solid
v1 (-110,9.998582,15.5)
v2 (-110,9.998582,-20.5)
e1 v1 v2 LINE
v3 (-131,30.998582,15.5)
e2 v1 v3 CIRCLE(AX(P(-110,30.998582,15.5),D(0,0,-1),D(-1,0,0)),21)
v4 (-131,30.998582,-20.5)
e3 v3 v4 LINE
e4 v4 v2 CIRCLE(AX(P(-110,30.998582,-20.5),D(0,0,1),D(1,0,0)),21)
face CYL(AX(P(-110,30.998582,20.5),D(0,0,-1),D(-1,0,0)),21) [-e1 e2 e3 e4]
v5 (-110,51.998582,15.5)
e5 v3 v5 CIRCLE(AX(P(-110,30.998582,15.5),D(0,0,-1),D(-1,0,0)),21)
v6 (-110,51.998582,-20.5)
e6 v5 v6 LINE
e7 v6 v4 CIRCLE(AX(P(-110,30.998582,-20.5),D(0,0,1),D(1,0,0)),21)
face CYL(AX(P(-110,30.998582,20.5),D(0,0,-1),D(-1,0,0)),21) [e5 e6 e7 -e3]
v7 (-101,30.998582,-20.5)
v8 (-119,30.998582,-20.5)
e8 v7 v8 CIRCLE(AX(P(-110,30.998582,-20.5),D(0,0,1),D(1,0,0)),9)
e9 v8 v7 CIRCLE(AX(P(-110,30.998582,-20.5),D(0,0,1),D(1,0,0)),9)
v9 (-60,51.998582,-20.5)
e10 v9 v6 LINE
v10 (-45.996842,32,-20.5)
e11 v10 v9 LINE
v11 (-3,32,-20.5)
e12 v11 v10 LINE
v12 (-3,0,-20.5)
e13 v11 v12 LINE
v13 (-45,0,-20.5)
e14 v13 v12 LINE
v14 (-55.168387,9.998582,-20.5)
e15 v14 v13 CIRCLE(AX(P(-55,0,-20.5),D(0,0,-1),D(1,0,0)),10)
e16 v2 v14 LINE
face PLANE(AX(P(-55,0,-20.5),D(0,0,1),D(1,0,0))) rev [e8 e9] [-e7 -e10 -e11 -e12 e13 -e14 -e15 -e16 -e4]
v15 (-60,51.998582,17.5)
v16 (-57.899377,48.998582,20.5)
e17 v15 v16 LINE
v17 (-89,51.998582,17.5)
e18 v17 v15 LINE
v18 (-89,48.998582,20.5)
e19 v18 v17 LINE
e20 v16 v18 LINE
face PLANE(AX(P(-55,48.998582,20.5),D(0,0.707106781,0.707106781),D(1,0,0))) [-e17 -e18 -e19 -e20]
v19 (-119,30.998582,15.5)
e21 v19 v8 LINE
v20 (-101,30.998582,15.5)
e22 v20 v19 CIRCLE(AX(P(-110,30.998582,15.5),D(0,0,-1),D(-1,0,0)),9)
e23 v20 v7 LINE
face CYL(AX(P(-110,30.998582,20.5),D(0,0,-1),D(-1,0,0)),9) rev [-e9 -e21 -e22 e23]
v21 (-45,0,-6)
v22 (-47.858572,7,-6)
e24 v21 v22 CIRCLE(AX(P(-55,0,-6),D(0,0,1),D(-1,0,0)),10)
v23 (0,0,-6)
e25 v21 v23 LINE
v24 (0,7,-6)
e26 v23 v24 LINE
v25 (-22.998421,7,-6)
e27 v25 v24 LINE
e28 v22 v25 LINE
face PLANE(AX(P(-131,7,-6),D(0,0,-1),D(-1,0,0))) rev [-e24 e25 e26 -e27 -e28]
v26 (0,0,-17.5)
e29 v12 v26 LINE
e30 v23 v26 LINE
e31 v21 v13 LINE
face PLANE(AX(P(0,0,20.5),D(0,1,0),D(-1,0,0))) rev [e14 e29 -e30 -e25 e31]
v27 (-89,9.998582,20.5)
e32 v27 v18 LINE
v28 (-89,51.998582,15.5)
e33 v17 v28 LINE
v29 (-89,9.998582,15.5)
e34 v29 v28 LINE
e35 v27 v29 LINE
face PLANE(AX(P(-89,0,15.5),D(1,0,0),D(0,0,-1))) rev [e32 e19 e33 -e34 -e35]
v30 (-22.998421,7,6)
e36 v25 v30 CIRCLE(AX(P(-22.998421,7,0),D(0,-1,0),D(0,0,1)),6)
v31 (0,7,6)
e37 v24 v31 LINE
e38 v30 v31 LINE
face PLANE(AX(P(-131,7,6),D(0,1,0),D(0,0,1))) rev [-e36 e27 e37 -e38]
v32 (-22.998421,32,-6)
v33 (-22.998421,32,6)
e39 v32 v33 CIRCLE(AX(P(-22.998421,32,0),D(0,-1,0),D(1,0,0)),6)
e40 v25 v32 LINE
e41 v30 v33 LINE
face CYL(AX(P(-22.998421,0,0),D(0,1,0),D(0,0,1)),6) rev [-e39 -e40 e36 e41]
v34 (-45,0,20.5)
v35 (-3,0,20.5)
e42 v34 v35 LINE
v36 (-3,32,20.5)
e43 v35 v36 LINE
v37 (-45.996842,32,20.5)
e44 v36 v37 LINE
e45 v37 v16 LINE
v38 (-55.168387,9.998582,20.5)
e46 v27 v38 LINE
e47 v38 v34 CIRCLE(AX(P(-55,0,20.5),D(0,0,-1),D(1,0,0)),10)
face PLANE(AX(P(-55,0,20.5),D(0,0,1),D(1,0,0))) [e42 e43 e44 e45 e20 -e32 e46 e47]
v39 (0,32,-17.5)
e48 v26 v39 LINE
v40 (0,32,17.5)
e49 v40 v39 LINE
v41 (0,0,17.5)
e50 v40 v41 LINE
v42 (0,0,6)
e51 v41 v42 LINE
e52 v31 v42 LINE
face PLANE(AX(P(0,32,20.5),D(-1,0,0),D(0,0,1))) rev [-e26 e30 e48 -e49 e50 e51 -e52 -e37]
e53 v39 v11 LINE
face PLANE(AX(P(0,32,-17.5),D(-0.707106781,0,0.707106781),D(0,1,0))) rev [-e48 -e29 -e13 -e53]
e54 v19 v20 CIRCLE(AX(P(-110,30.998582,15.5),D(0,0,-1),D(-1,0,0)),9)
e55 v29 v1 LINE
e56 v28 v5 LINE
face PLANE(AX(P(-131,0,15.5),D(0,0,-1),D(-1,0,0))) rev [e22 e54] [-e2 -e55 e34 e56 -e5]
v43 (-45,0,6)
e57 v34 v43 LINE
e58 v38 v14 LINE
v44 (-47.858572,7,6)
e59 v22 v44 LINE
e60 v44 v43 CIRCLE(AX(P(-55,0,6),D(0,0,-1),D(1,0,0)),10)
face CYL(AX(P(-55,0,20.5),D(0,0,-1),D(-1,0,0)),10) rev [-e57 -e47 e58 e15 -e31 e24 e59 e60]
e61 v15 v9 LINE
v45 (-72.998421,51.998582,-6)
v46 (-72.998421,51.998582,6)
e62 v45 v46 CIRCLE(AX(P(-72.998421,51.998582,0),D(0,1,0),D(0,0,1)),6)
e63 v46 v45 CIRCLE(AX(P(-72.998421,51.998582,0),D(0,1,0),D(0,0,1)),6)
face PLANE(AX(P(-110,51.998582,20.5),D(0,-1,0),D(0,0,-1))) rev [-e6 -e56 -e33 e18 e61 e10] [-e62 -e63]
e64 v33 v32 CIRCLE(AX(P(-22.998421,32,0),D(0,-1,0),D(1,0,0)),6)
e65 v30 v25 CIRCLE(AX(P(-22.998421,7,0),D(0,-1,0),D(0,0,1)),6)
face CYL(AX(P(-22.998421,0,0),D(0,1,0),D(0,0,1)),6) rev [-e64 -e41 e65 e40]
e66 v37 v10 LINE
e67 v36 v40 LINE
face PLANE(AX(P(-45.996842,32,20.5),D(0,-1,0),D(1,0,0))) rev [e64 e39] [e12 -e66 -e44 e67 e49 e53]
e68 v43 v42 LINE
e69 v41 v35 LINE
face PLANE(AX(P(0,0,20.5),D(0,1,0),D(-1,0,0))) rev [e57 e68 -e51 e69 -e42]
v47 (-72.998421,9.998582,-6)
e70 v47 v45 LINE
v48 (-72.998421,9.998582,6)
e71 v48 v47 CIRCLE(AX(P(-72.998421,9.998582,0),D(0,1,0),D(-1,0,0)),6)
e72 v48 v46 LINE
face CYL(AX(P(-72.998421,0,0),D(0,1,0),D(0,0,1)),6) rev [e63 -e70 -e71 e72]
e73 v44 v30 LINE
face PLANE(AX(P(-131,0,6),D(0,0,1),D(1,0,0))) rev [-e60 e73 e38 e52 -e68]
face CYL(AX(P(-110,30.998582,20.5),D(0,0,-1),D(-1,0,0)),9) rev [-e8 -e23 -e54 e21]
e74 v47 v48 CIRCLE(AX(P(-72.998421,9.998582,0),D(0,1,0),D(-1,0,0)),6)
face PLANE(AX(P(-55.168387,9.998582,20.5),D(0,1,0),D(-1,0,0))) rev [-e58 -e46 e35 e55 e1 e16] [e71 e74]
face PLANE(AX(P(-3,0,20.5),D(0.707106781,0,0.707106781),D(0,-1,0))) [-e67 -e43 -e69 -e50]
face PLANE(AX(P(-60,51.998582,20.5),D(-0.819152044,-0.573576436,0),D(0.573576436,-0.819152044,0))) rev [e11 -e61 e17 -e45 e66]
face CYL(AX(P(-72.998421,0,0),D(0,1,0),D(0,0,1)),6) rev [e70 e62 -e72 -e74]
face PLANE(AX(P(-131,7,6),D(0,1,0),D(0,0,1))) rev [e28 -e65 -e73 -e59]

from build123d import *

# Parameters (mm, degrees)
BRACKET_SIDE_PROFILE_SKETCH_R = 9
BRACKET_BODY_41MM_DEPTH       = 20.5
TOP_FACE_CUTS_SKETCH_R        = 6
TOP_FACE_CUTS_SKETCH_W        = 42
TOP_FACE_CUTS_SKETCH_H        = 5
TOP_FACE_CUTS_DEPTH           = 143.425779095
END_SLOT_SKETCH_W             = 12
END_SLOT_SKETCH_H             = 7
END_SLOT_12MM_DEPTH           = 143.425779095
EDGE_CHAMFER_3MM_SIZE         = 3


with BuildPart() as part:
    # Bracket Side Profile Sketch → Bracket Body 41mm (new, symmetric)
    with BuildSketch(Plane.XY):
        with BuildLine():
            Line((0, 0), (-45, 0))
            ThreePointArc((-45, 0), (-47.988718556, 7.130352903), (-55.168386504, 9.998582199))
            Line((-55.168386504, 9.998582199), (-86.000956968, 9.998582199))
            Line((-86.000956968, 9.998582199), (-110, 9.998582199))
            ThreePointArc((-110, 9.998582199), (-131, 30.998582199), (-110, 51.998582199))
            Line((-110, 51.998582199), (-85.996841991, 51.998582199))
            Line((-85.996841991, 51.998582199), (-60, 51.998582199))
            Line((-60, 51.998582199), (-45.996841991, 32))
            Line((-45.996841991, 32), (0, 32))
            Line((0, 32), (0, 0))
        make_face()
        with Locations((-110, 30.998582199)):
            Circle(BRACKET_SIDE_PROFILE_SKETCH_R, mode=Mode.SUBTRACT)
    extrude(amount=BRACKET_BODY_41MM_DEPTH, both=True)

    # Top Face Cuts Sketch → Top Face Cuts (cut, through all)
    with BuildSketch(Plane(origin=(0, 51.998582199, 0), x_dir=(1, 0, 0), z_dir=(0, 1, 0))):
        with Locations(Location((-72.998420995, 0, 0), (0, 0, 270))):
            Circle(TOP_FACE_CUTS_SKETCH_R)
        with Locations(Location((-22.998420995, 0, 0), (0, 0, 270))):
            Circle(TOP_FACE_CUTS_SKETCH_R)
        with Locations((-110, -18)):
            Rectangle(TOP_FACE_CUTS_SKETCH_W, TOP_FACE_CUTS_SKETCH_H)
    extrude(amount=-TOP_FACE_CUTS_DEPTH, mode=Mode.SUBTRACT)

    # End Slot Sketch → End Slot 12mm (cut, through all)
    with BuildSketch(Plane(origin=(0, 0, 0), x_dir=(0, 0, -1), z_dir=(1, 0, 0))):
        with Locations((0, 3.5)):
            Rectangle(END_SLOT_SKETCH_W, END_SLOT_SKETCH_H)
    extrude(amount=-END_SLOT_12MM_DEPTH, mode=Mode.SUBTRACT)

    # Edge Chamfer 3mm
    edge_chamfer_3mm_edges = [part.edges().sort_by_distance(p)[0] for p in [
        (0, 16, -20.5),
        (-74.5, 51.998582199, 20.5),
        (0, 16, 20.5),
    ]]
    chamfer(edge_chamfer_3mm_edges, length=EDGE_CHAMFER_3MM_SIZE)


solid = part.part
